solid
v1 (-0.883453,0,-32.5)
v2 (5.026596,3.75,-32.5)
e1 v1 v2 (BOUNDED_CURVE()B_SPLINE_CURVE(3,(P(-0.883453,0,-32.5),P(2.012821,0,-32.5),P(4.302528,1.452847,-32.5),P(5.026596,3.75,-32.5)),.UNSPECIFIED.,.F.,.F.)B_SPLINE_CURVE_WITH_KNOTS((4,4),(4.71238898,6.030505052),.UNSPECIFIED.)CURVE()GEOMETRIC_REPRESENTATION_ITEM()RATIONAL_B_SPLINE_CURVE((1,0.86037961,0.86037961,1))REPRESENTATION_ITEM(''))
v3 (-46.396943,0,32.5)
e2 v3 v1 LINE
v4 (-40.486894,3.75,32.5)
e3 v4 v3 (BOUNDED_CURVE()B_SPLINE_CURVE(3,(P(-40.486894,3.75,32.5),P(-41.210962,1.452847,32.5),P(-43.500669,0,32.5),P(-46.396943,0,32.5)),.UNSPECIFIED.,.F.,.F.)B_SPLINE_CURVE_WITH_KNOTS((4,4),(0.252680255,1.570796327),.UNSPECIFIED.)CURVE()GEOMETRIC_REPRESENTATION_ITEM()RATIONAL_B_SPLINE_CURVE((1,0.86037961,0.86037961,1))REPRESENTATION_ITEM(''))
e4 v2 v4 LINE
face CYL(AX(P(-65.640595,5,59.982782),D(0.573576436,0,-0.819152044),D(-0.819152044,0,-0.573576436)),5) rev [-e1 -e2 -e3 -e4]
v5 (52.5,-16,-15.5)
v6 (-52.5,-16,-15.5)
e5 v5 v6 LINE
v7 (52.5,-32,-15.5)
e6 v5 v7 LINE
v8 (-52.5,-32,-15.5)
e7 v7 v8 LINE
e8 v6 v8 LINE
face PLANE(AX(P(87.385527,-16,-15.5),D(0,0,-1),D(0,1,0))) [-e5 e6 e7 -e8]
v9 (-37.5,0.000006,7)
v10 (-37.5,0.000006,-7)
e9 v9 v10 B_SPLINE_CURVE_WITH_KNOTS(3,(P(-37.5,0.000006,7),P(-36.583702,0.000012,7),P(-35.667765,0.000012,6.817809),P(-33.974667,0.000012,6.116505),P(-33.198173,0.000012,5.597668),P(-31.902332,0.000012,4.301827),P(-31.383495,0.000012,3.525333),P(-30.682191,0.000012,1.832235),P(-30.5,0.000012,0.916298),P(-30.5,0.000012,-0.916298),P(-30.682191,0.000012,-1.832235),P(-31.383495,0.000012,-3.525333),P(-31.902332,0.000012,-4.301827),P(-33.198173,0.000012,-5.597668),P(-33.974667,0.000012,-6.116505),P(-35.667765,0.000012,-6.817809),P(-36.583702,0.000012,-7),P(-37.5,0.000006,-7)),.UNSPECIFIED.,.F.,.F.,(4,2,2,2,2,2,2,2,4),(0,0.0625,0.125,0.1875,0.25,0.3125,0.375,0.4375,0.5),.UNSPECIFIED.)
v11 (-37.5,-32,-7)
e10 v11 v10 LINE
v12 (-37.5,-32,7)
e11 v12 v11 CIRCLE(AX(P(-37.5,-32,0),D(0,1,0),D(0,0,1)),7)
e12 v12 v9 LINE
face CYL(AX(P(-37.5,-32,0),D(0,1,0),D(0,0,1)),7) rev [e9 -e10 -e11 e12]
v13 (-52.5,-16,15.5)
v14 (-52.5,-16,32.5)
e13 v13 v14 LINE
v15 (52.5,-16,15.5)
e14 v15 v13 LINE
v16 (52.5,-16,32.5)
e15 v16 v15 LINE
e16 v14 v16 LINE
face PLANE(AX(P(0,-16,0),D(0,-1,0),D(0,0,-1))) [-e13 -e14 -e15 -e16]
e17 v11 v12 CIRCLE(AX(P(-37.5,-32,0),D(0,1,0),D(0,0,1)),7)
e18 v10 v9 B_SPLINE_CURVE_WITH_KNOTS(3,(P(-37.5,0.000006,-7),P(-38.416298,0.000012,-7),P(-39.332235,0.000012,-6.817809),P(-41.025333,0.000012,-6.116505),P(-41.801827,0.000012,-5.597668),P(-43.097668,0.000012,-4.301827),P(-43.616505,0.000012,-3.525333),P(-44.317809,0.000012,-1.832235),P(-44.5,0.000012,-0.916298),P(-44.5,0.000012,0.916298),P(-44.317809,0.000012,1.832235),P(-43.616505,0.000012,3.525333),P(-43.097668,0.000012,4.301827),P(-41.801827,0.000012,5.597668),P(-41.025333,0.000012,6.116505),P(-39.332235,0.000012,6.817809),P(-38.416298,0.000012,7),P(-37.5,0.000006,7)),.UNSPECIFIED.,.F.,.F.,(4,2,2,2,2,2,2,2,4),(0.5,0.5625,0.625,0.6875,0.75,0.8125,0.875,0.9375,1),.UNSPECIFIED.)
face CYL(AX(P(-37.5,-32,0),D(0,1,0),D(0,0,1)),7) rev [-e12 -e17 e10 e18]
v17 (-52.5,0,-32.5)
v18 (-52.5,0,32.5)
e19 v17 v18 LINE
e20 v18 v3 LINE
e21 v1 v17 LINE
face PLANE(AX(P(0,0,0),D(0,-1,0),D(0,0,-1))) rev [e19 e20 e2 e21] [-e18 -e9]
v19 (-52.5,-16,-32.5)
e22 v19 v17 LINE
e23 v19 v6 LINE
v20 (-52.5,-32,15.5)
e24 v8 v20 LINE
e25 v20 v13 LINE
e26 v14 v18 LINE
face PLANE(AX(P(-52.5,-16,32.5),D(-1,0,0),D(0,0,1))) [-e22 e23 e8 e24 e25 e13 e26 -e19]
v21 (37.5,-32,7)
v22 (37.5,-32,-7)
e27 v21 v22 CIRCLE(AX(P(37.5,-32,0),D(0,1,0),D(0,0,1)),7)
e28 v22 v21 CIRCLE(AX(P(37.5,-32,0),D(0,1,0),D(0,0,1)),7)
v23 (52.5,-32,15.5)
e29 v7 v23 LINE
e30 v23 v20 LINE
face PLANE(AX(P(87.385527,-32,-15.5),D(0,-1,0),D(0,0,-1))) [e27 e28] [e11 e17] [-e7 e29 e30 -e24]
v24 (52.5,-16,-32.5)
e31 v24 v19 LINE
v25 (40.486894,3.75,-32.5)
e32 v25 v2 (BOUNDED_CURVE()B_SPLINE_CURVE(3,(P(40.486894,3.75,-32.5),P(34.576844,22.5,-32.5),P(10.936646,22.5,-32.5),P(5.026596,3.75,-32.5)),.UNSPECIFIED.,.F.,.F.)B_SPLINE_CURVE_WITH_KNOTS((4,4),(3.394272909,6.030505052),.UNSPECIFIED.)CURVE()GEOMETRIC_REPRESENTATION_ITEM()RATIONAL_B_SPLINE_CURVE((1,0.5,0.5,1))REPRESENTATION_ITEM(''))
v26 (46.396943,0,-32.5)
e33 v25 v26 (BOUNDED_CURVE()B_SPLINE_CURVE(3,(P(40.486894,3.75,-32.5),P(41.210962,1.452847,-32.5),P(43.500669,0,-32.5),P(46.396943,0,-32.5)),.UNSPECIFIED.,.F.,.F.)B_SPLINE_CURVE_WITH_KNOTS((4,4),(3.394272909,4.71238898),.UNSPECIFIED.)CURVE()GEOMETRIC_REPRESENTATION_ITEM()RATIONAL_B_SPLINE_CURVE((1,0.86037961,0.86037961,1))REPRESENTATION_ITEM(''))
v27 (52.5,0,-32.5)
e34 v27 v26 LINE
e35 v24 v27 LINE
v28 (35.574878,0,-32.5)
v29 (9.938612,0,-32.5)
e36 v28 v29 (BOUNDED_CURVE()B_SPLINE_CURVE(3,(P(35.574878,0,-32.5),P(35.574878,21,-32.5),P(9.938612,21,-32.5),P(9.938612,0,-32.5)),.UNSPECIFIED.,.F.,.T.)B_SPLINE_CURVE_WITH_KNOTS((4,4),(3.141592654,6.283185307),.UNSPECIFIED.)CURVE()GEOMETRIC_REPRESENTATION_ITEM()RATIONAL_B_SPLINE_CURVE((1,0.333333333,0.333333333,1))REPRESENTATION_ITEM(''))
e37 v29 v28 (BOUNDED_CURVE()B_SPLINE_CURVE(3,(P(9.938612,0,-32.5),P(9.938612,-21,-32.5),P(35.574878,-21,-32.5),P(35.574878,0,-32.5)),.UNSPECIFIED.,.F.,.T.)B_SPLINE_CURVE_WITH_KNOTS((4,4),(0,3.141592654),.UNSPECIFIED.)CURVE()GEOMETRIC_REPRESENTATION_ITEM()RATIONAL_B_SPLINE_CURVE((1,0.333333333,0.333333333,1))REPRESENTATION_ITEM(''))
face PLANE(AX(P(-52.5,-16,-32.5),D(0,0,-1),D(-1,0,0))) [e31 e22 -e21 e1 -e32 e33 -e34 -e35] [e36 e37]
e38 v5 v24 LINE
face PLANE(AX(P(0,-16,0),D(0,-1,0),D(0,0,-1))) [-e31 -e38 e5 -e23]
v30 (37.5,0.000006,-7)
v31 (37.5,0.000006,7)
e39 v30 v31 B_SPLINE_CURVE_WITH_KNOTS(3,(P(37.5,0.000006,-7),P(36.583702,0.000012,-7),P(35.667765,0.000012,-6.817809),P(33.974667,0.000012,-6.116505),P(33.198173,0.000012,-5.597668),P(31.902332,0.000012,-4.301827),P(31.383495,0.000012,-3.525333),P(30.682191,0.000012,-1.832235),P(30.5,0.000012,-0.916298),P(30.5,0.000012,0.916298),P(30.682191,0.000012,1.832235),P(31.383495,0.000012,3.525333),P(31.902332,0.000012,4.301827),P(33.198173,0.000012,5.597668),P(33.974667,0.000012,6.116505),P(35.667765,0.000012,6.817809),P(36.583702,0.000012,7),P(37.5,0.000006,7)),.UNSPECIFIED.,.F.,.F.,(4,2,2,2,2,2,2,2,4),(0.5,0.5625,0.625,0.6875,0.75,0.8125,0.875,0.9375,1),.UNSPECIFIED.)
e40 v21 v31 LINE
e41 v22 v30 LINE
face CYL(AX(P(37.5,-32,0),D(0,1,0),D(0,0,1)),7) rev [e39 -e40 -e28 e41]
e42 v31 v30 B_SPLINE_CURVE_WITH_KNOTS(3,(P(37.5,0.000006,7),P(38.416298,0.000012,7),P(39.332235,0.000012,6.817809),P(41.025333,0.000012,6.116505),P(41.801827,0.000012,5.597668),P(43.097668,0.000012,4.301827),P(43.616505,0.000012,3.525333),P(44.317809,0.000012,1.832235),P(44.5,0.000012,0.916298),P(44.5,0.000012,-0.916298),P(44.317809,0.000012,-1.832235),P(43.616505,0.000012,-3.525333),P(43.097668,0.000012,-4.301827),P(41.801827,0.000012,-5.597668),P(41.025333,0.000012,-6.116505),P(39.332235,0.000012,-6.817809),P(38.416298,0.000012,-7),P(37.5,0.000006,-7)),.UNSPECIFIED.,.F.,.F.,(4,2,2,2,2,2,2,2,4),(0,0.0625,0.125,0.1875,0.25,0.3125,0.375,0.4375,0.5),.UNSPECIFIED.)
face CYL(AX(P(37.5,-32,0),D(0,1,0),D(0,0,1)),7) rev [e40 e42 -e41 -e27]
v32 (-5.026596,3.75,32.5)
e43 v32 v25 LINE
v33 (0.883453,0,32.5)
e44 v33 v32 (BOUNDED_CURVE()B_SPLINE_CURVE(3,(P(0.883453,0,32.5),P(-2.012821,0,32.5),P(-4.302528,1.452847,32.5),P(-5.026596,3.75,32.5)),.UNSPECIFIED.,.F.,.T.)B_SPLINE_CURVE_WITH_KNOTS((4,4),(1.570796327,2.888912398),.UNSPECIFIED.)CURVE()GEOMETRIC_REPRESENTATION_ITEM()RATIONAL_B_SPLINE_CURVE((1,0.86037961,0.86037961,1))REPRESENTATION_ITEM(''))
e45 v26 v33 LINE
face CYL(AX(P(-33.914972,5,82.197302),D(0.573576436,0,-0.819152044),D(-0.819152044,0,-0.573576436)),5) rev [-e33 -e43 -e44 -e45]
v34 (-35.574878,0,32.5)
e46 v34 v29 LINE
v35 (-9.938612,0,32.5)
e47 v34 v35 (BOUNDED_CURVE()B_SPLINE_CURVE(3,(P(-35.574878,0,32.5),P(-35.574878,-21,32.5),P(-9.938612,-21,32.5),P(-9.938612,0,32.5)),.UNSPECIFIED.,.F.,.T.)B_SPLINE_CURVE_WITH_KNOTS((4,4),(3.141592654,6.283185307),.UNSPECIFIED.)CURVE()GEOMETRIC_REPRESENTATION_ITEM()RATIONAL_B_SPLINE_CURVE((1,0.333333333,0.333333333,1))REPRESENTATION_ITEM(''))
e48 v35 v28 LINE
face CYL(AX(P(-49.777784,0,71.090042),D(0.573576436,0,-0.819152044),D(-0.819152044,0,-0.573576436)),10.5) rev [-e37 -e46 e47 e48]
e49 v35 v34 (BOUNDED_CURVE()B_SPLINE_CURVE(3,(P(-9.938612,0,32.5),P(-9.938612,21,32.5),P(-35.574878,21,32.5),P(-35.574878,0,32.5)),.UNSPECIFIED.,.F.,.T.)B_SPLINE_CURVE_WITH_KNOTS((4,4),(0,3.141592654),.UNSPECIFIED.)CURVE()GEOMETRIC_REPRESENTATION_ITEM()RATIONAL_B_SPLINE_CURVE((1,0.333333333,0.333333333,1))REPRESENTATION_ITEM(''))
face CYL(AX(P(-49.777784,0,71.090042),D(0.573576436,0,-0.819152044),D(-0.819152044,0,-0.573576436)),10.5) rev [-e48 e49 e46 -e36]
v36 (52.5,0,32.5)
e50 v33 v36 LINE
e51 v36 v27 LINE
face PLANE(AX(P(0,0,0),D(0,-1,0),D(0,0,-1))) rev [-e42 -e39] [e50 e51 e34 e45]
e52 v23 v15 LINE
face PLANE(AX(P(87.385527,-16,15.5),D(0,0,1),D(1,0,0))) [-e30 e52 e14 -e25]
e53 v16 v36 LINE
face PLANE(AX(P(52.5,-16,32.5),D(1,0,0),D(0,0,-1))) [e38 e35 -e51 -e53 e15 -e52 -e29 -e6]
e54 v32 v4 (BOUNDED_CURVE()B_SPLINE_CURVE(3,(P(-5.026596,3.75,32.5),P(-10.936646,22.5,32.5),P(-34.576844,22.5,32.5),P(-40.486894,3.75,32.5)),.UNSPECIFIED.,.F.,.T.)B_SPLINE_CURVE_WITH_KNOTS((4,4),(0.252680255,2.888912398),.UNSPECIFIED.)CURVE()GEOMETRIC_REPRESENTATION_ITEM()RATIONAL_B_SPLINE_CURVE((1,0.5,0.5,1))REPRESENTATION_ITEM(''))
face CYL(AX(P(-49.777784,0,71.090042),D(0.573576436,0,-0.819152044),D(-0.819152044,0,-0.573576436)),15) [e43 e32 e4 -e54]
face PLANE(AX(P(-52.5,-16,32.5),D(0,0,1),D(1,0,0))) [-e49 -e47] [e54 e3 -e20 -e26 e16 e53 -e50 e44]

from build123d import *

# Parameters (mm, degrees)
BASE_PLATE_SKETCH_W                      = 105
BASE_PLATE_SKETCH_H                      = 65
BASE_PLATE_DEPTH                         = 16
LOCATING_KEY_SKETCH_W                    = 31
LOCATING_KEY_SKETCH_H                    = 16
LOCATING_KEY_DEPTH                       = 105
MOUNTING_HOLES_DEPTH                     = 70.544949493
MOUNTING_HOLES_DEPTH_BACK                = 70.544949493
MOUNTING_HOLES_SKETCH_R                  = 7
INCLINED_CYLINDER_BOSS_REACH             = 71.545
BOSS_PROFILE_SKETCH_R                    = 15
BOSS_PROFILE_SKETCH_R_2                  = 10.5
INCLINED_CYLINDER_BOSS_DIRECTION_2_REACH = 71.545
BOSS_BORE_DEPTH                          = 70.544949493
BOSS_BORE_DEPTH_BACK                     = 70.544949493
BOSS_BORE_SKETCH_R                       = 10.5
BOSS_BLEND_FILLET_R5_R                   = 5


with BuildPart() as part:
    # Base Plate Sketch → Base Plate (new body)
    with BuildSketch(Plane(origin=(0, 0, 0), x_dir=(1, 0, 0), z_dir=(0, 1, 0))):
        Rectangle(BASE_PLATE_SKETCH_W, BASE_PLATE_SKETCH_H)
    extrude(amount=-BASE_PLATE_DEPTH)

    # Locating Key Sketch → Locating Key (add)
    with BuildSketch(Plane.ZY.offset(52.5)):
        with Locations((0, -24)):
            Rectangle(LOCATING_KEY_SKETCH_W, LOCATING_KEY_SKETCH_H)
    extrude(amount=-LOCATING_KEY_DEPTH)

    # Mounting Holes Sketch → Mounting Holes (cut, two sides: drawn at the far end of the back side and taken through both)
    with BuildSketch(Plane(origin=(0, 0, 0), x_dir=(1, 0, 0), z_dir=(0, 1, 0)).offset(-MOUNTING_HOLES_DEPTH_BACK)):
        with Locations(Location((-37.5, 0, 0), (0, 0, 270))):
            Circle(MOUNTING_HOLES_SKETCH_R)
        with Locations(Location((37.5, 0, 0), (0, 0, 270))):
            Circle(MOUNTING_HOLES_SKETCH_R)
    extrude(amount=MOUNTING_HOLES_DEPTH + MOUNTING_HOLES_DEPTH_BACK, mode=Mode.SUBTRACT)

    # Inclined Cylinder Boss: up to this plane
    inclined_cylinder_boss_end = Plane(origin=(-52.5, -16, 32.5), z_dir=(0, 0, 1))
    # Boss Profile Sketch → Inclined Cylinder Boss (add, up to the surface)
    with BuildSketch(Plane(origin=(0, 0, 0), x_dir=(0.819152044288991, 0, 0.5735764363510473), z_dir=(-0.5735764363510473, 0, 0.819152044288991)), mode=Mode.PRIVATE) as inclined_cylinder_boss_sk1:
        Circle(BOSS_PROFILE_SKETCH_R)
        Circle(BOSS_PROFILE_SKETCH_R_2, mode=Mode.SUBTRACT)
    inclined_cylinder_boss_tool1 = split(extrude(inclined_cylinder_boss_sk1.sketch, amount=INCLINED_CYLINDER_BOSS_REACH, mode=Mode.PRIVATE), bisect_by=inclined_cylinder_boss_end, keep=Keep.BOTH, mode=Mode.PRIVATE)
    add(inclined_cylinder_boss_tool1.solids().sort_by_distance((-11.939744, 0, -8.360299))[0])

    # Inclined Cylinder Boss direction 2: up to this plane
    inclined_cylinder_boss_direction_2_end = Plane(origin=(-52.5, -16, -32.5), z_dir=(0, 0, -1))
    # Boss Profile Sketch → Inclined Cylinder Boss direction 2 (add, up to the surface)
    with BuildSketch(Plane(origin=(0, 0, 0), x_dir=(0.819152044288991, 0, 0.5735764363510473), z_dir=(-0.5735764363510473, 0, 0.819152044288991)), mode=Mode.PRIVATE) as inclined_cylinder_boss_direction_2_sk1:
        Circle(BOSS_PROFILE_SKETCH_R)
        Circle(BOSS_PROFILE_SKETCH_R_2, mode=Mode.SUBTRACT)
    inclined_cylinder_boss_direction_2_tool1 = split(extrude(inclined_cylinder_boss_direction_2_sk1.sketch, amount=-INCLINED_CYLINDER_BOSS_DIRECTION_2_REACH, mode=Mode.PRIVATE), bisect_by=inclined_cylinder_boss_direction_2_end, keep=Keep.BOTH, mode=Mode.PRIVATE)
    add(inclined_cylinder_boss_direction_2_tool1.solids().sort_by_distance((-11.939744, 0, -8.360299))[0])

    # Boss Bore Sketch → Boss Bore (cut, two sides: drawn at the far end of the back side and taken through both)
    with BuildSketch(Plane(origin=(0, 0, 0), x_dir=(0.819152044288991, 0, 0.5735764363510473), z_dir=(-0.5735764363510473, 0, 0.819152044288991)).offset(-BOSS_BORE_DEPTH_BACK)):
        with Locations(Location((0, 0, 0), (0, 0, 180))):
            Circle(BOSS_BORE_SKETCH_R)
    extrude(amount=BOSS_BORE_DEPTH + BOSS_BORE_DEPTH_BACK, mode=Mode.SUBTRACT)

    # Boss Blend Fillet R5
    boss_blend_fillet_r5_edges = [part.edges().sort_by_distance(p)[0] for p in [
        (-18.311618831, 0, 0),
        (18.311618831, 0, 0),
    ]]
    fillet(boss_blend_fillet_r5_edges, radius=BOSS_BLEND_FILLET_R5_R)


solid = part.part
